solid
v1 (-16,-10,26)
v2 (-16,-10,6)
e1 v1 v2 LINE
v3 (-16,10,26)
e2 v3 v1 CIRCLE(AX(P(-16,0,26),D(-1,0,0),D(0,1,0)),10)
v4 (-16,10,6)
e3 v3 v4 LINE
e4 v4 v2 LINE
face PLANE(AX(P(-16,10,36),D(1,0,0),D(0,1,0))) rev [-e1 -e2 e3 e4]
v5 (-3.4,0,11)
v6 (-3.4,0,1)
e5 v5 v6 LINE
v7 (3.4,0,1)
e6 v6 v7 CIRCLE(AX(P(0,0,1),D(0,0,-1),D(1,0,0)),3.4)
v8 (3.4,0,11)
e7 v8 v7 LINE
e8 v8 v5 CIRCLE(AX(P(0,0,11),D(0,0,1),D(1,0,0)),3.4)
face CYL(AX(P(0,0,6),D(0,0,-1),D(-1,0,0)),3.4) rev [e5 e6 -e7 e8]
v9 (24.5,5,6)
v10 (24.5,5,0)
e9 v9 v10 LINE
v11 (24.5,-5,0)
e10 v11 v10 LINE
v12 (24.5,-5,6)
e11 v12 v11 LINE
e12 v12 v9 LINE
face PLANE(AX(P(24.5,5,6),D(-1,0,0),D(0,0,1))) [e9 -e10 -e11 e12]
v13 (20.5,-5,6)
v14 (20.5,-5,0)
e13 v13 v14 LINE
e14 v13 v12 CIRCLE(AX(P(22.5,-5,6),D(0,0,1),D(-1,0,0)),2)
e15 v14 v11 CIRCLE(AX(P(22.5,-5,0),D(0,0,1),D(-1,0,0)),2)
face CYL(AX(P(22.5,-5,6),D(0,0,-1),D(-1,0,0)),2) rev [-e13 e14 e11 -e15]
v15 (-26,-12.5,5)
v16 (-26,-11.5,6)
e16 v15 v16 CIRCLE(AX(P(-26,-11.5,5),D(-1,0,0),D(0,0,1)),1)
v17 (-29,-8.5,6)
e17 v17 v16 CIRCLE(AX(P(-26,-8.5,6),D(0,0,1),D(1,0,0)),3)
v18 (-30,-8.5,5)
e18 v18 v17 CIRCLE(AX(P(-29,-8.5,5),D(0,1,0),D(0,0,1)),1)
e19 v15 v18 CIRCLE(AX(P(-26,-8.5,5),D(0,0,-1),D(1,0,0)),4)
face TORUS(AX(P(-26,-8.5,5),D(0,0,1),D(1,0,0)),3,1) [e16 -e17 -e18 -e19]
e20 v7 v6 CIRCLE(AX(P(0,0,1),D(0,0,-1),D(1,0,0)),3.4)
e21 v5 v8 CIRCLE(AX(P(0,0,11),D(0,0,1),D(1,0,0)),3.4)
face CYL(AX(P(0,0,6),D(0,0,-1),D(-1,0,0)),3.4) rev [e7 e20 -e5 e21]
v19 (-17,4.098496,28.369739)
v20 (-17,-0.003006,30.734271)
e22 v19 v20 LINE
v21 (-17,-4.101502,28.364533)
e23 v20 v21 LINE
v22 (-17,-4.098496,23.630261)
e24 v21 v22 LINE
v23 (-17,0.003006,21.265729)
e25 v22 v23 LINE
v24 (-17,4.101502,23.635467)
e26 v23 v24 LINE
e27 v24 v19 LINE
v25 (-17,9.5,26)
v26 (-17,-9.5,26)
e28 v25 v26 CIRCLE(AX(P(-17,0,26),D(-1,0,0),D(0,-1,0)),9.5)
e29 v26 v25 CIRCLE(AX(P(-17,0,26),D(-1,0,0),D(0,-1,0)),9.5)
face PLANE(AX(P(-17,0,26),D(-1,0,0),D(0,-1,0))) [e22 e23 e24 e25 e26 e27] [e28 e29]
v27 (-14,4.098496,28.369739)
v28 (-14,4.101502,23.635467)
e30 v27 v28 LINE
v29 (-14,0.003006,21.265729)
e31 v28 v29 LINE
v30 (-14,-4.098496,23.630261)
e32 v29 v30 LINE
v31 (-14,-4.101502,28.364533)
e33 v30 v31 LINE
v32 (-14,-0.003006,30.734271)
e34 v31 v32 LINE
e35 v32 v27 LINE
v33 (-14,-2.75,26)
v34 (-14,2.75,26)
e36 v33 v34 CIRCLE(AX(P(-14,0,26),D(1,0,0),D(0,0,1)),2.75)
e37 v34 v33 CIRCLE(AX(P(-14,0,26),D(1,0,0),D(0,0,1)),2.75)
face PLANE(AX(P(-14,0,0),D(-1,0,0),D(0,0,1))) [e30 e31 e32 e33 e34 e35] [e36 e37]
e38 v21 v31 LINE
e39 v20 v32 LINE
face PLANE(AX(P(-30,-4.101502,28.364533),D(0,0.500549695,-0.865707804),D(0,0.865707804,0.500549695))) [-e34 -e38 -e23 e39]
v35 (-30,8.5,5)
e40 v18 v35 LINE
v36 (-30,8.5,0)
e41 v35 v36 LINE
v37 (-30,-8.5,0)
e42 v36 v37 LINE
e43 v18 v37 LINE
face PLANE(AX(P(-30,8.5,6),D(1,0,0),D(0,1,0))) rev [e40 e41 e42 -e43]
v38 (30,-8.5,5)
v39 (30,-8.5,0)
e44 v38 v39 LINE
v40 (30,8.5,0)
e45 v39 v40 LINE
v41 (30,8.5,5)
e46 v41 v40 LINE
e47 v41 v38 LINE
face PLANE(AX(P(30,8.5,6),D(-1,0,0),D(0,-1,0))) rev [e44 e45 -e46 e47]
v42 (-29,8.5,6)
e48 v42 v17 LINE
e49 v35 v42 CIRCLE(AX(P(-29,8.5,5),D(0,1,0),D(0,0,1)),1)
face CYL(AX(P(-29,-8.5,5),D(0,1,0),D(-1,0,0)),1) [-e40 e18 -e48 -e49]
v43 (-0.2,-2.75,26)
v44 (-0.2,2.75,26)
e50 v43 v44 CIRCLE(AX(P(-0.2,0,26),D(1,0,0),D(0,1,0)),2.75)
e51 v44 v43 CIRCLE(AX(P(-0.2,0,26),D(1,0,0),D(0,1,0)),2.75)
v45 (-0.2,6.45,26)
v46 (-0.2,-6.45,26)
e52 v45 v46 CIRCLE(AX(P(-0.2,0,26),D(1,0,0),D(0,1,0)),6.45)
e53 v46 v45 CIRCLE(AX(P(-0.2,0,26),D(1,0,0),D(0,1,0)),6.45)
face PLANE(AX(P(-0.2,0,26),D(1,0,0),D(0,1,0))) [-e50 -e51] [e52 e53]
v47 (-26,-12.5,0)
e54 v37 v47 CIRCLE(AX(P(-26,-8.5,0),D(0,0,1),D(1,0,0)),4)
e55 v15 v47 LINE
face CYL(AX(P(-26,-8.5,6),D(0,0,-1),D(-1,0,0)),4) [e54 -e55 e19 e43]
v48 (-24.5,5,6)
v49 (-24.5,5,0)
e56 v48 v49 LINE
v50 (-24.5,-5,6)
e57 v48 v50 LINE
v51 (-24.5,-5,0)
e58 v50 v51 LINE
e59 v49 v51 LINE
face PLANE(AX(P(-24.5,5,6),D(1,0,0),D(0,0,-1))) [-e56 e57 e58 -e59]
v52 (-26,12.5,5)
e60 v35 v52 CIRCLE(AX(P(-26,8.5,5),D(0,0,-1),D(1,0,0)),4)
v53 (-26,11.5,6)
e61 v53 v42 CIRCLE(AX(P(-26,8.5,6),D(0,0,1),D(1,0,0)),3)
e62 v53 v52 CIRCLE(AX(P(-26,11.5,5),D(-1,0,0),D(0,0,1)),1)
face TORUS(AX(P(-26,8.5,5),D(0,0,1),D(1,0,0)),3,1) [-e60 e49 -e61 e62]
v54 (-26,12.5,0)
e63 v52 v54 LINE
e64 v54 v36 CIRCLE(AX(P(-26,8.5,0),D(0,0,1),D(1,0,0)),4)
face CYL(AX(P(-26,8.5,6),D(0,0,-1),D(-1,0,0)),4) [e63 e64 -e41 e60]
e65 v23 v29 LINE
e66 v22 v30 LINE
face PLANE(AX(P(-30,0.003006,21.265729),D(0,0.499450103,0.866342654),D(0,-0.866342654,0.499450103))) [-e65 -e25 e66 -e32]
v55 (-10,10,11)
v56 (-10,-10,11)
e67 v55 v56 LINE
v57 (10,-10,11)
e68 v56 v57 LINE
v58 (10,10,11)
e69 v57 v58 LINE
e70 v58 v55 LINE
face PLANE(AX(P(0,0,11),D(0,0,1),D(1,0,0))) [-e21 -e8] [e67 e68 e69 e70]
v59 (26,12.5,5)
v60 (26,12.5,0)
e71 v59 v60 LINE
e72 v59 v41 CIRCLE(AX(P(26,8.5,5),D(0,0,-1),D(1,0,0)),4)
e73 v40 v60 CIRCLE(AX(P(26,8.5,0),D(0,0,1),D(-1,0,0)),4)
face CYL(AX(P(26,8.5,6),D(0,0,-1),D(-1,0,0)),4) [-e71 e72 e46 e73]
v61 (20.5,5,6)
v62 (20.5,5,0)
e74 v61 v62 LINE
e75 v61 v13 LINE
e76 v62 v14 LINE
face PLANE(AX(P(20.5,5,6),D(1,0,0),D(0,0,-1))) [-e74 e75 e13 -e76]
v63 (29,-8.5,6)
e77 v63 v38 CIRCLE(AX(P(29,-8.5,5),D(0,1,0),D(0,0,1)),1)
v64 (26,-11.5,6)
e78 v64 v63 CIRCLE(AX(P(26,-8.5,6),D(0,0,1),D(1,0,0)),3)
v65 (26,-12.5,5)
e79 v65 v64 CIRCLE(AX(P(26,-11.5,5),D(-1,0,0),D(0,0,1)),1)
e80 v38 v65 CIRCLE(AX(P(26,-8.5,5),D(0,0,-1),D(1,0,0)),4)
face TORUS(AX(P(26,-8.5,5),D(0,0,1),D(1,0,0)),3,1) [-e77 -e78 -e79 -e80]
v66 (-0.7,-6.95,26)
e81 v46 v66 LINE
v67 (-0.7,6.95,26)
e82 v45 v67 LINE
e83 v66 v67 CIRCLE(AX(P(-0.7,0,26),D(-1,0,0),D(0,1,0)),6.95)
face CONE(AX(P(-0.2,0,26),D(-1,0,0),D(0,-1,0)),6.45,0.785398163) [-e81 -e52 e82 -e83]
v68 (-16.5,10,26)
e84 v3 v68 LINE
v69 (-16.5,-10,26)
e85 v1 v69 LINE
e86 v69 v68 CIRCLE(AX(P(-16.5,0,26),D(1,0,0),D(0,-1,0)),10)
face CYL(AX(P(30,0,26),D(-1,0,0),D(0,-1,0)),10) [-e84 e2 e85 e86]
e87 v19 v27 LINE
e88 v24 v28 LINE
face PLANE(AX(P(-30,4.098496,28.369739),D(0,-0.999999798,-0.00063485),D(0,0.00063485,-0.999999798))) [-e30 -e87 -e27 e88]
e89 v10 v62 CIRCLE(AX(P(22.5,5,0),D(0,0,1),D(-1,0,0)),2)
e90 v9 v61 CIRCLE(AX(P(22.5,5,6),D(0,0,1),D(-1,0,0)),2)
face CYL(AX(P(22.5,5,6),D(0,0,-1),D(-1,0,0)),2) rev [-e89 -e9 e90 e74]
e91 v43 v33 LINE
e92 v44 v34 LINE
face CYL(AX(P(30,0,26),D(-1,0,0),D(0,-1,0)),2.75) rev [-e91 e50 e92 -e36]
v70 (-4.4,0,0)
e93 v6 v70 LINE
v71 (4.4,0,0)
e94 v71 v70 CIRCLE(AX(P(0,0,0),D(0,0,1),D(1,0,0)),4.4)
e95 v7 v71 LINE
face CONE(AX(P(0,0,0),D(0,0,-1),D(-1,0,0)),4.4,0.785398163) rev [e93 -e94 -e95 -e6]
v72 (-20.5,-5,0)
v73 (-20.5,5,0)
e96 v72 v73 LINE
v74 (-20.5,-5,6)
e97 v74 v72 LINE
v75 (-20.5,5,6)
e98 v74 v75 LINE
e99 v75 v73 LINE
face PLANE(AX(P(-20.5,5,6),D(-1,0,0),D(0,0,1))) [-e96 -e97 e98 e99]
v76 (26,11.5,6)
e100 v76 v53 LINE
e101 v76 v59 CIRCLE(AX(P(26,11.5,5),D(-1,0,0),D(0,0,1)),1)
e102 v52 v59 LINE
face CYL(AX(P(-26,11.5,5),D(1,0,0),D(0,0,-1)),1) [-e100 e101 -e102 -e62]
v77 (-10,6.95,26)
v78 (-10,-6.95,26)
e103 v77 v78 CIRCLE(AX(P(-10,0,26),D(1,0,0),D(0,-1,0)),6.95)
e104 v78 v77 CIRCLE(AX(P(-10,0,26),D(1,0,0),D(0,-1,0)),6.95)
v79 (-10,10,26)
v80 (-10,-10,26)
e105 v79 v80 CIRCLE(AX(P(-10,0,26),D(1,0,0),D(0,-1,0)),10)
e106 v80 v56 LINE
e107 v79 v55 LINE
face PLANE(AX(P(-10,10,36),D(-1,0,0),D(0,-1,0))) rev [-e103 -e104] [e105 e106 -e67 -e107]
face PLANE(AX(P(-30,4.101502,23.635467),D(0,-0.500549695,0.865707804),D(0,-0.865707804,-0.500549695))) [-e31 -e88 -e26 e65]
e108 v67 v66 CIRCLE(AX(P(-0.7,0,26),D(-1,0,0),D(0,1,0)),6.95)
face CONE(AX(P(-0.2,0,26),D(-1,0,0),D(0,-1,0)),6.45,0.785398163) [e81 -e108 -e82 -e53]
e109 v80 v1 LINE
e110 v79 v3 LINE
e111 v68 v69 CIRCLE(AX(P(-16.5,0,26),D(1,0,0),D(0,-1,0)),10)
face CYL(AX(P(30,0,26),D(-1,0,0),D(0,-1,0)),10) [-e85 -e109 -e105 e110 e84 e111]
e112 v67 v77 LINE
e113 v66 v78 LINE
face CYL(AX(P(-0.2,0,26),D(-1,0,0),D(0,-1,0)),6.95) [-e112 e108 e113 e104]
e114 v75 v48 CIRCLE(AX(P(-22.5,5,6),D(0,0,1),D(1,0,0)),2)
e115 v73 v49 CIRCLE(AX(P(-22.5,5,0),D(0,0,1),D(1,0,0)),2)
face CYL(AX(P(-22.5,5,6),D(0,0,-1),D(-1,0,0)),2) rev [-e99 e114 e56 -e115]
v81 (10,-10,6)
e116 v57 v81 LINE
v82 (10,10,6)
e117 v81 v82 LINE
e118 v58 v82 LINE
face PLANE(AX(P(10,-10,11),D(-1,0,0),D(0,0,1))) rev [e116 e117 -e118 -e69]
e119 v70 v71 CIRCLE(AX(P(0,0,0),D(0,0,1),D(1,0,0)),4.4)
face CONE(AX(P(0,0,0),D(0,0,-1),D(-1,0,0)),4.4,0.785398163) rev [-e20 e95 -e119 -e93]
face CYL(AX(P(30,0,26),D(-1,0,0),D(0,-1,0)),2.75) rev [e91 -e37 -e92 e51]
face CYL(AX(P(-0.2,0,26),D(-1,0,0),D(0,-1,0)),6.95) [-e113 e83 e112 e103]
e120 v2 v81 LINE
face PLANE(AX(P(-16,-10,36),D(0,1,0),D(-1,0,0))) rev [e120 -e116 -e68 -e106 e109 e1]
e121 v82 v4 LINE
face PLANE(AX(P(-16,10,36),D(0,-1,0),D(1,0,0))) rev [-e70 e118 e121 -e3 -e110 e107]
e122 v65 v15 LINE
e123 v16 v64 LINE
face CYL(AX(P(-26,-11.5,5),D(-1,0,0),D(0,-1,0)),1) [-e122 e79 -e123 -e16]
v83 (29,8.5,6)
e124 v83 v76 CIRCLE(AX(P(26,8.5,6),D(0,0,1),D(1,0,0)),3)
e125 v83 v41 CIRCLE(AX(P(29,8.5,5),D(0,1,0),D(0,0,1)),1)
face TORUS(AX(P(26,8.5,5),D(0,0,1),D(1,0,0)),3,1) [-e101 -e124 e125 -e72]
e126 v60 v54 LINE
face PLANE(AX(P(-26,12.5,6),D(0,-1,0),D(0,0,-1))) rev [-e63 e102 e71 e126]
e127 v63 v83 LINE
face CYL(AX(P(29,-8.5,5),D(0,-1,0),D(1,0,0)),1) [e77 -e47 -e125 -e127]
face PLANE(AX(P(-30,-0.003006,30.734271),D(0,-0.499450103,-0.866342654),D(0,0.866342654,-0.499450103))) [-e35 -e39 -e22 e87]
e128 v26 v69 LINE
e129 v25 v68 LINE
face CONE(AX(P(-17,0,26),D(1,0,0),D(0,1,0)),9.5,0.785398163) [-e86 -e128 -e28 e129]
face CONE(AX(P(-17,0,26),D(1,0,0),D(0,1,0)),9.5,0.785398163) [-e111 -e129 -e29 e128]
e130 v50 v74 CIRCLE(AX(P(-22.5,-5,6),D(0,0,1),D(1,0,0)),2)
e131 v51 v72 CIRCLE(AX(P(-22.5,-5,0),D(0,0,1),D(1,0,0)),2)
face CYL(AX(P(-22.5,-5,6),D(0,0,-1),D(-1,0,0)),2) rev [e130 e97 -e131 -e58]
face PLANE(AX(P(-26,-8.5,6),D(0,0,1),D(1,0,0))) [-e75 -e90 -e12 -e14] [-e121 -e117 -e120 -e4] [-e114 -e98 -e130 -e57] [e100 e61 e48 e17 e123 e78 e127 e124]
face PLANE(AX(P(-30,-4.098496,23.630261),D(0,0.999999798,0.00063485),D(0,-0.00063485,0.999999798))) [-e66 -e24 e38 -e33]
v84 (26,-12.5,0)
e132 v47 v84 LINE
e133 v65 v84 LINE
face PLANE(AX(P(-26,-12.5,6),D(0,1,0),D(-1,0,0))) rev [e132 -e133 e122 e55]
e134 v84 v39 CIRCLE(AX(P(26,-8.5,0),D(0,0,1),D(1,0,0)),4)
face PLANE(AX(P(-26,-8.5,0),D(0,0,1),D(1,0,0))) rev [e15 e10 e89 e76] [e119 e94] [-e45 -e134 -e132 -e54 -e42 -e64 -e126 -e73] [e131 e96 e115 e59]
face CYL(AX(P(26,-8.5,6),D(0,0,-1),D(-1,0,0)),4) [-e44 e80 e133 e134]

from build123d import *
from build123d.topology import SkipClean

# Parameters (mm, degrees)
SKETCH1_R               = 3.4
BOSS_EXTRUDE1_DEPTH     = 6
CHAMFER1_SIZE           = 1
SKETCH2_W               = 6
SKETCH2_H               = 20
BOSS_EXTRUDE2_DEPTH     = 30
CUT_EXTRUDE1_DEPTH      = 60.73483071
CUT_EXTRUDE1_DEPTH_BACK = 60.73483071
SKETCH3_R               = 2.75
SKETCH4_R               = 10
SKETCH4_R_2             = 2.75
BOSS_EXTRUDE3_DEPTH     = 1
CHAMFER2_SIZE           = 0.5
FILLET1_R               = 1
SKETCH5_W               = 20
SKETCH5_H               = 20
SKETCH5_R               = 3.4
BOSS_EXTRUDE4_DEPTH     = 5
CUT_EXTRUDE2_DEPTH      = 61.508263976
CUT_EXTRUDE2_DEPTH_BACK = 3
SKETCH7_R               = 6.95
SKETCH7_R_2             = 2.75
BOSS_EXTRUDE5_DEPTH     = 9.8
CHAMFER4_SIZE           = 0.5


with BuildPart() as part:
    # Sketch1 → Boss-Extrude1 (new body)
    with BuildSketch(Plane.XY):
        with BuildLine():
            Line((-26, 12.5), (26, 12.5))
            ThreePointArc((26, 12.5), (28.828427125, 11.328427125), (30, 8.5))
            Line((30, 8.5), (30, -8.5))
            ThreePointArc((30, -8.5), (28.828427125, -11.328427125), (26, -12.5))
            Line((26, -12.5), (-26, -12.5))
            ThreePointArc((-26, -12.5), (-28.828427125, -11.328427125), (-30, -8.5))
            Line((-30, -8.5), (-30, 8.5))
            ThreePointArc((-30, 8.5), (-28.828427125, 11.328427125), (-26, 12.5))
        make_face()
        Circle(SKETCH1_R, mode=Mode.SUBTRACT)
        with BuildLine():
            Line((-20.5, 5), (-20.5, -5))
            ThreePointArc((-20.5, -5), (-22.5, -7), (-24.5, -5))
            Line((-24.5, -5), (-24.5, 5))
            ThreePointArc((-24.5, 5), (-22.5, 7), (-20.5, 5))
        make_face(mode=Mode.SUBTRACT)
        with BuildLine():
            Line((20.5, 5), (20.5, -5))
            ThreePointArc((20.5, -5), (22.5, -7), (24.5, -5))
            Line((24.5, -5), (24.5, 5))
            ThreePointArc((24.5, 5), (22.5, 7), (20.5, 5))
        make_face(mode=Mode.SUBTRACT)
    extrude(amount=BOSS_EXTRUDE1_DEPTH)

    # Chamfer1
    chamfer1_edges = [part.edges().sort_by_distance(p)[0] for p in [
        (-3.4, 0, 0),
    ]]
    chamfer(chamfer1_edges, length=CHAMFER1_SIZE)

    # Sketch2 → Boss-Extrude2 (add)
    with BuildSketch(Plane.XY.offset(6)):
        with Locations((-13, 0)):
            Rectangle(SKETCH2_W, SKETCH2_H)
    extrude(amount=BOSS_EXTRUDE2_DEPTH)

    # Sketch3 → Cut-Extrude1 (cut, two sides: drawn at the far end of the back side and taken through both)
    with BuildSketch(Plane.ZY.offset(16).offset(-CUT_EXTRUDE1_DEPTH_BACK)):
        with Locations(Location((26, 0, 0), (0, 0, 270))):
            Circle(SKETCH3_R)
        with BuildLine():
            Line((26, 10), (26.394492089, 15.308450708))
            Line((26.394492089, 15.308450708), (43.333609146, 9.271325943))
            Line((43.333609146, 9.271325943), (37.706774414, -17.690590479))
            Line((37.706774414, -17.690590479), (26, -10))
            ThreePointArc((26, -10), (36, 0), (26, 10))
        make_face()
    extrude(amount=CUT_EXTRUDE1_DEPTH + CUT_EXTRUDE1_DEPTH_BACK, mode=Mode.SUBTRACT)

    # Sketch4 → Boss-Extrude3 (add, symmetric)
    with BuildSketch(Plane.ZY.offset(16)):
        with Locations(Location((26, 0, 0), (0, 0, 270))):
            Circle(SKETCH4_R)
        with Locations(Location((26, 0, 0), (0, 0, 270))):
            Circle(SKETCH4_R_2, mode=Mode.SUBTRACT)
    extrude(amount=BOSS_EXTRUDE3_DEPTH, both=True)

    # Chamfer2
    chamfer2_edges = [part.edges().sort_by_distance(p)[0] for p in [
        (-17, 10, 26),
    ]]
    chamfer(chamfer2_edges, length=CHAMFER2_SIZE)

    # Fillet1
    fillet1_edges = [part.edges().sort_by_distance(p)[0] for p in [
        (28.828427125, -11.328427125, 6),
        (30, 0, 6),
        (28.828427125, 11.328427125, 6),
        (0, 12.5, 6),
        (-28.828427125, 11.328427125, 6),
        (-30, 0, 6),
        (-28.828427125, -11.328427125, 6),
        (0, -12.5, 6),
    ]]
    fillet(fillet1_edges, radius=FILLET1_R)

    # Sketch5 → Boss-Extrude4 (add)
    with BuildSketch(Plane.XY.offset(6)):
        Rectangle(SKETCH5_W, SKETCH5_H)
        Circle(SKETCH5_R, mode=Mode.SUBTRACT)
    extrude(amount=BOSS_EXTRUDE4_DEPTH)

    # Sketch6 → Cut-Extrude2 (cut, two sides: drawn at the far end of the back side and taken through both)
    with BuildSketch(Plane.ZY.offset(17).offset(-CUT_EXTRUDE2_DEPTH_BACK)):
        Polygon((28.369738511, 4.098496398), (23.635467258, 4.10150195), (21.265728747, 0.003005552), (23.630261489, -4.098496398), (28.364532742, -4.10150195), (30.734271253, -0.003005552), align=None)
    extrude(amount=CUT_EXTRUDE2_DEPTH + CUT_EXTRUDE2_DEPTH_BACK, mode=Mode.SUBTRACT)

    # Sketch7 → Boss-Extrude5 (add)
    with SkipClean():  # the faces are left unmerged after this step: merging them gives an invalid solid
        with BuildSketch(Plane(origin=(-10, 0, 0), x_dir=(0, 0, -1), z_dir=(1, 0, 0))):
            with Locations(Location((-26, 0, 0), (0, 0, 270))):
                Circle(SKETCH7_R)
            with Locations(Location((-26, 0, 0), (0, 0, 180))):
                Circle(SKETCH7_R_2, mode=Mode.SUBTRACT)
        extrude(amount=BOSS_EXTRUDE5_DEPTH)

    # Chamfer4
    chamfer4_edges = [part.edges().sort_by_distance(p)[0] for p in [
        (-0.2, 6.95, 26),
    ]]
    chamfer(chamfer4_edges, length=CHAMFER4_SIZE)


solid = part.part
